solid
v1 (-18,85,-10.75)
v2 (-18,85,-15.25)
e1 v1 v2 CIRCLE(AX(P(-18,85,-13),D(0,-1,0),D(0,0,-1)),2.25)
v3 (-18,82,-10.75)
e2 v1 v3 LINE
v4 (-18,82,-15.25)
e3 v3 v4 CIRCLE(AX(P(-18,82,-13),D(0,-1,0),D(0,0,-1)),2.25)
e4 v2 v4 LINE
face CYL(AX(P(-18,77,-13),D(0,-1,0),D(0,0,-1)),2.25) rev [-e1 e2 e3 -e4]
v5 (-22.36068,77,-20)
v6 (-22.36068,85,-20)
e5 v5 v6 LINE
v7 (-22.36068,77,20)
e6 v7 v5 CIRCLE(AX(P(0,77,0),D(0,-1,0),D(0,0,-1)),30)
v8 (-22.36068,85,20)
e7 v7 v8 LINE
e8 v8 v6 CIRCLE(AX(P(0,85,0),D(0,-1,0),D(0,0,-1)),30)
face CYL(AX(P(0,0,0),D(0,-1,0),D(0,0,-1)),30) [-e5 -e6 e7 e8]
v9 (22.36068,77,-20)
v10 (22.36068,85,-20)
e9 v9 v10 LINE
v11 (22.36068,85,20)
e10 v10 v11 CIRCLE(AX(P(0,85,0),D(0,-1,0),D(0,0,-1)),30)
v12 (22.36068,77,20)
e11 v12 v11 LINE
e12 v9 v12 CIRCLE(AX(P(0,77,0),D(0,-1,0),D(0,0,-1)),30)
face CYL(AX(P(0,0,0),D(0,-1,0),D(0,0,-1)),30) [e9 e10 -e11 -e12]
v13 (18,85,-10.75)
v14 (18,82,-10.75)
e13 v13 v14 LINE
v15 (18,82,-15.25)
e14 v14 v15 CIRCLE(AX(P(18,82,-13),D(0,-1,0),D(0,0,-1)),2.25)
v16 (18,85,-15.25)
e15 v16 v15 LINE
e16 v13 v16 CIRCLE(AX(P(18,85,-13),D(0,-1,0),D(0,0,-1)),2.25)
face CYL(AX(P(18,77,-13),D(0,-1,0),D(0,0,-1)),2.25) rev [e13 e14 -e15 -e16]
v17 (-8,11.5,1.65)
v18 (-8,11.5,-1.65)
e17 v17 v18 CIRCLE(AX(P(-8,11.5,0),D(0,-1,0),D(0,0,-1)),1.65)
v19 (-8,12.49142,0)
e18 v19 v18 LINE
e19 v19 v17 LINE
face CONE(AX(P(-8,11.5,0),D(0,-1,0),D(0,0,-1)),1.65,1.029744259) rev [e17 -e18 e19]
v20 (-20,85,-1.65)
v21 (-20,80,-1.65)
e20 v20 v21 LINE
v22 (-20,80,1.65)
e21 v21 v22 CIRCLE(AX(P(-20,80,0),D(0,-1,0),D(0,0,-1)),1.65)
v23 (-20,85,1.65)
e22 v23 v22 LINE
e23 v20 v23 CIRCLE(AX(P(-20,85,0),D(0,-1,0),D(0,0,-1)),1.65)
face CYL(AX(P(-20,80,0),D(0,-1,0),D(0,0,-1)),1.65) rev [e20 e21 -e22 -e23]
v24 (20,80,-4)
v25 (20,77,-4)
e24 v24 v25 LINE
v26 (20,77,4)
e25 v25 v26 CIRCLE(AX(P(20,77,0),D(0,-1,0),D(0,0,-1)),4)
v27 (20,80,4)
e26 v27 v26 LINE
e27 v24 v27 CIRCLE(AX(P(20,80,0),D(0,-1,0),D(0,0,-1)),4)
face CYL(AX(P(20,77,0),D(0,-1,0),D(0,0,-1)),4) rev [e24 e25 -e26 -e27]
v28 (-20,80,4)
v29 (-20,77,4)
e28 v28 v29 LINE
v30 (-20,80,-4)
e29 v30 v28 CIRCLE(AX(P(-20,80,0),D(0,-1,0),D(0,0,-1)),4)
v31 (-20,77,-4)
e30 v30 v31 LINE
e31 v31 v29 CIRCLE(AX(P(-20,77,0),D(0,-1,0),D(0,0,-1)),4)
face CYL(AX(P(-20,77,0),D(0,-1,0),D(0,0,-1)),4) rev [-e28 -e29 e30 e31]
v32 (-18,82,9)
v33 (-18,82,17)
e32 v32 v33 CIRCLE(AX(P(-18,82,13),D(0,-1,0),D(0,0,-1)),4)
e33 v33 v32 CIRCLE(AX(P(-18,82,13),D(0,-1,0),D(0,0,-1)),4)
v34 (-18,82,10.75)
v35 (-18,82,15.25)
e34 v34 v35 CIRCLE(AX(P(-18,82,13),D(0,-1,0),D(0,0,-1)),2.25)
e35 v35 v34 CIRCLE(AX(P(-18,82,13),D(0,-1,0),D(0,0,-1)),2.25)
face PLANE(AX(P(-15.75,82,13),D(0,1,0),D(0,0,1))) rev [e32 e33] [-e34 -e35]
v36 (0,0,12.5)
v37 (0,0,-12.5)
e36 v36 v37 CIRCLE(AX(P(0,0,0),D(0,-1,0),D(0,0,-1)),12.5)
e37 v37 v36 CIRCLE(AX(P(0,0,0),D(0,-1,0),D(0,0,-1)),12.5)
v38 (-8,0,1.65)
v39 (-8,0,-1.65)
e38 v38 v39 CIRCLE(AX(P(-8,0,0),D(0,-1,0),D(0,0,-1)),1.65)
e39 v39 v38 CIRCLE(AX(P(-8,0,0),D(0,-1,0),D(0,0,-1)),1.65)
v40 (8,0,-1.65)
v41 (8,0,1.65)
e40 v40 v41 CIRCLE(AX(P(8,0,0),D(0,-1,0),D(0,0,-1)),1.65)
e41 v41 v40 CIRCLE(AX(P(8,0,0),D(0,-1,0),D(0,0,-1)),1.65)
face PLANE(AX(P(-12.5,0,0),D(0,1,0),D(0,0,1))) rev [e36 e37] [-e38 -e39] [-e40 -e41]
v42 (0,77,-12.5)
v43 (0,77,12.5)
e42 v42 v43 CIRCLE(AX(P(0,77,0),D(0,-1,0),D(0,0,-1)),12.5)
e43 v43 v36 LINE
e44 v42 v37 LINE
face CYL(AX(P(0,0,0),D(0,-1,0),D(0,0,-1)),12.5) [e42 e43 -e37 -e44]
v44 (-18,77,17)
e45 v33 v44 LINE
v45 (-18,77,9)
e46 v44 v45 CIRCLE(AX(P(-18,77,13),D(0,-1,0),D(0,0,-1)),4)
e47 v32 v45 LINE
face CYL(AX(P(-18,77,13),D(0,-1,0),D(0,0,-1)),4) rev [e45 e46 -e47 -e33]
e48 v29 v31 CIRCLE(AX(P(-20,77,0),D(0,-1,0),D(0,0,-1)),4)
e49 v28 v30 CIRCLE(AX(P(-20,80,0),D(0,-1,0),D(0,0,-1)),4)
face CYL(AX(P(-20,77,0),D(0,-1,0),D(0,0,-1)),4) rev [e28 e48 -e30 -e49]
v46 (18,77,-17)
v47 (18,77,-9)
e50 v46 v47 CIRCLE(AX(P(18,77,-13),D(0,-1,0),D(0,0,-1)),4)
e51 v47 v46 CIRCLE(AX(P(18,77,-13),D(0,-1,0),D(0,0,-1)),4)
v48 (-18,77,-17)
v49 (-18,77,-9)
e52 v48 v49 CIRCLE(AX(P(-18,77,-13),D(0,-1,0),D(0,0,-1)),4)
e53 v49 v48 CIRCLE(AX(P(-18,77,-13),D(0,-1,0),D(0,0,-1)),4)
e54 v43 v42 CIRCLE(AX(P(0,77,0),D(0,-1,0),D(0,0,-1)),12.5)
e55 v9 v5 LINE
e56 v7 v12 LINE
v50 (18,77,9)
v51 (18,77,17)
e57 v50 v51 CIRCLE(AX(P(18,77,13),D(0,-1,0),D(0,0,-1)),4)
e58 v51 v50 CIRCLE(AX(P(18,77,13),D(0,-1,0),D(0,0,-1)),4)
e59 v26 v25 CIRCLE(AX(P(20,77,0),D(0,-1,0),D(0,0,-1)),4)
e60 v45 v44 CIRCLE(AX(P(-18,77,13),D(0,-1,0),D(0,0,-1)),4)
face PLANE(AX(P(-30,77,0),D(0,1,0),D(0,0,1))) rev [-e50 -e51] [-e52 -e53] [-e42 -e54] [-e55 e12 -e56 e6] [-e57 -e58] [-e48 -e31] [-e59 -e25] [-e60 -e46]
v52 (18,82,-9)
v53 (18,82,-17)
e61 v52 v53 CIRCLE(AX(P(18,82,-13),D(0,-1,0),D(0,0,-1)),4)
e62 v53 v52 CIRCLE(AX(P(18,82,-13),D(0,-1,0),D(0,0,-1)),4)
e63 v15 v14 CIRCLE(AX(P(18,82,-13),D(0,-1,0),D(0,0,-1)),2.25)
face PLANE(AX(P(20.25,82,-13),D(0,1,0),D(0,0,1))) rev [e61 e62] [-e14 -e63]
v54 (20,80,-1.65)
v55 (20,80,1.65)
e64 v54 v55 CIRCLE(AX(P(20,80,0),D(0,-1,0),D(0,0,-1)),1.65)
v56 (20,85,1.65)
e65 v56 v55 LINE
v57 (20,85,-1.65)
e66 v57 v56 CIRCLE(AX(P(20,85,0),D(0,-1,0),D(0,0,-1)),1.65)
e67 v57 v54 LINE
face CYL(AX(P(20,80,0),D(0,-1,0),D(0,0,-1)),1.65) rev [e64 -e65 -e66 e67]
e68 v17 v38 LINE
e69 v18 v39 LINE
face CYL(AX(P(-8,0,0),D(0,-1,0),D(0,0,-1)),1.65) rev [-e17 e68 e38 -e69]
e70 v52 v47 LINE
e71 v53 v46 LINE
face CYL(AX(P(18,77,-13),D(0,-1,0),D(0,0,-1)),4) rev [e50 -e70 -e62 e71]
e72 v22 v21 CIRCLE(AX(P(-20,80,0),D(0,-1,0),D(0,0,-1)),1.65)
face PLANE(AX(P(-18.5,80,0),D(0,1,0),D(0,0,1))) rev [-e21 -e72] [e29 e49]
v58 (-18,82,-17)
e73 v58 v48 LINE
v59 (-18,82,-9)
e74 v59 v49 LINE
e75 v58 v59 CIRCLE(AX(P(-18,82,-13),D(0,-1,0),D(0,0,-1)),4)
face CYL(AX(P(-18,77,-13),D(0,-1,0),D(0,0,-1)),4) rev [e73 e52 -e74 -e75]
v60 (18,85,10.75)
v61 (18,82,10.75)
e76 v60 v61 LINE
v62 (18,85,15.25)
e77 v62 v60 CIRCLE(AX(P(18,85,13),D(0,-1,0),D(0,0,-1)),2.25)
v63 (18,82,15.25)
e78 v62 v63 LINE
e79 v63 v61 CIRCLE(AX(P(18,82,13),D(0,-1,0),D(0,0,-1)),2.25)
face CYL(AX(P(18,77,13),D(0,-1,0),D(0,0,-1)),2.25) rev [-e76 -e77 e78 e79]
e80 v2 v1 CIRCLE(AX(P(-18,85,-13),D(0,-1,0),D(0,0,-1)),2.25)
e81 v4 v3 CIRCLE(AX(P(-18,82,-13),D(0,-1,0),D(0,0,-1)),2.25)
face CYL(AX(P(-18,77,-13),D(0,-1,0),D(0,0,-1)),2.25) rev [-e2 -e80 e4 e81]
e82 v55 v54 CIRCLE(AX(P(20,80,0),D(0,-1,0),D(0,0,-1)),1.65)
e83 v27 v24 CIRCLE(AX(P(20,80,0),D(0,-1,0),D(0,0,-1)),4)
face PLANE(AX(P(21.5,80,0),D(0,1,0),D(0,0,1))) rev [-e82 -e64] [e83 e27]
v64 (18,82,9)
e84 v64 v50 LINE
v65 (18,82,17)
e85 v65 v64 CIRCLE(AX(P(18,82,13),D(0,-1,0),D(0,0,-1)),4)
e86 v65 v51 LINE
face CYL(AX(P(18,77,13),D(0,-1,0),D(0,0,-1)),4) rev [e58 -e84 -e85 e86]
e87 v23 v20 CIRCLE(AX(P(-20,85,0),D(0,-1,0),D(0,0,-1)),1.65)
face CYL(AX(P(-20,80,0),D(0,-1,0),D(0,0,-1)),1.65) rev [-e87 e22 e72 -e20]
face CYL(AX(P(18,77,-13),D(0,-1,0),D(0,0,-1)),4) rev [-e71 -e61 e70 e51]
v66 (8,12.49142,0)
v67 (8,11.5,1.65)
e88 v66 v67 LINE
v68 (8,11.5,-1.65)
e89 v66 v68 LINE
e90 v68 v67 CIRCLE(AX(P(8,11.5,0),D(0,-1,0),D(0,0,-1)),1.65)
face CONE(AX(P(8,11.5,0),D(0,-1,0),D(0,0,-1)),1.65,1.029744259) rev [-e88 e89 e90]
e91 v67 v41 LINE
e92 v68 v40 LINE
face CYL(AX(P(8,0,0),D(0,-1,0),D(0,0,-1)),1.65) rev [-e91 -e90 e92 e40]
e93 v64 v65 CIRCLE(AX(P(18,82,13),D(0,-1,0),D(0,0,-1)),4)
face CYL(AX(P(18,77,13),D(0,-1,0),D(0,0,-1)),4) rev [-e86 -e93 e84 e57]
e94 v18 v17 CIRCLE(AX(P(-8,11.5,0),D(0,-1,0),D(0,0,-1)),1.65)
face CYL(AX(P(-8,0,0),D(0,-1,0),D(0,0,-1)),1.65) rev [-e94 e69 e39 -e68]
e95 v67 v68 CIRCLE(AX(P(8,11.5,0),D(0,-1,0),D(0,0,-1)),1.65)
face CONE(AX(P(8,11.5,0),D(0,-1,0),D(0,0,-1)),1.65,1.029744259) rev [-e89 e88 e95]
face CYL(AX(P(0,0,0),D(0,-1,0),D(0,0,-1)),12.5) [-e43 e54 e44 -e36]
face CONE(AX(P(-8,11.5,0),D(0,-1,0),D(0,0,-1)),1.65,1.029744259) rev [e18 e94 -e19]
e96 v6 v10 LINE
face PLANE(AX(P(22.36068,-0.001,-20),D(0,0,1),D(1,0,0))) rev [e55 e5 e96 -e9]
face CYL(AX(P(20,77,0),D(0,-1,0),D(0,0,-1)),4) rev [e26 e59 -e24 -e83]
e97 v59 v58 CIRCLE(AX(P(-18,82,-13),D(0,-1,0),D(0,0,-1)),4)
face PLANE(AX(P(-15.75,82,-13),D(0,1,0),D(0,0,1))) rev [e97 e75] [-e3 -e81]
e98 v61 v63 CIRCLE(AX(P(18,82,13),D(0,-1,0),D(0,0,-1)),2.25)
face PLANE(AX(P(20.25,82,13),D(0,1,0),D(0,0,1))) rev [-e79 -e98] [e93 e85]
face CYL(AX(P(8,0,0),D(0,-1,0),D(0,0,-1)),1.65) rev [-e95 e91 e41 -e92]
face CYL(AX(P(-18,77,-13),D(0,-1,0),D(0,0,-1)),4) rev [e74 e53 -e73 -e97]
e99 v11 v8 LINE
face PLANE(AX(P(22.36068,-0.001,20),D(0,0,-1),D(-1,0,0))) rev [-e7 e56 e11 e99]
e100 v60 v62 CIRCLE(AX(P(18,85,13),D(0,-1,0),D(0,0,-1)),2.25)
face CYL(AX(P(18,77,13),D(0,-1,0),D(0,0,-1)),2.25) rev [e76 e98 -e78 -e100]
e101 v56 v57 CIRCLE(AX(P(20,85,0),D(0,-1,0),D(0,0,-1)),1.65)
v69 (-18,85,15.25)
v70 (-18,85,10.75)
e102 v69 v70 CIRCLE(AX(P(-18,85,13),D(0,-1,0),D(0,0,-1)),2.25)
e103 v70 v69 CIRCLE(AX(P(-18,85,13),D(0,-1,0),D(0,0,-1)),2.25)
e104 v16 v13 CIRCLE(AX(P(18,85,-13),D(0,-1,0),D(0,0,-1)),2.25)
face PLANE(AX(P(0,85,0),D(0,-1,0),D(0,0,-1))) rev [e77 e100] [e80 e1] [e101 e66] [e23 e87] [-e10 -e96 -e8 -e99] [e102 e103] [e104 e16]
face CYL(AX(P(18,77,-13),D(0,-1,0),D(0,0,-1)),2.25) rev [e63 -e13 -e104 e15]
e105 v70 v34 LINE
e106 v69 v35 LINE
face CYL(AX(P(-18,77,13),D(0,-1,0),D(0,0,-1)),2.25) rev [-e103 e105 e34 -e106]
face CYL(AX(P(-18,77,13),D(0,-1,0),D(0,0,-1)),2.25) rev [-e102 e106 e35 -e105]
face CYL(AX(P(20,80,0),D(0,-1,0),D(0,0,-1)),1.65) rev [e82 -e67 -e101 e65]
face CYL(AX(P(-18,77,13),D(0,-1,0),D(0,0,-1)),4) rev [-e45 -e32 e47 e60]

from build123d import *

# Parameters (mm, degrees)
M4_TAPPED_HOLE1_D                       = 3.3
M4_TAPPED_HOLE1_DEPTH                   = 11.5
M4_TAPPED_HOLE1_TIP                     = 0.991420021
CUT_EXTRUDE2_REACH                      = 97
CBORE_FOR_M4_HEX_HEAD_BOLT1_D           = 3
CBORE_FOR_M4_HEX_HEAD_BOLT1_CBORE_D     = 8
CBORE_FOR_M4_HEX_HEAD_BOLT1_CBORE_DEPTH = 3
M4_TAPPED_HOLE4_D                       = 3.3
M4_TAPPED_HOLE4_DEPTH                   = 10.1
M4_TAPPED_HOLE4_TIP                     = 0.991420021
CBORE_FOR_M4_HEX_HEAD_BOLT2_D           = 4.5
CBORE_FOR_M4_HEX_HEAD_BOLT2_DEPTH       = 10.1
CBORE_FOR_M4_HEX_HEAD_BOLT2_CBORE_D     = 8
CBORE_FOR_M4_HEX_HEAD_BOLT2_CBORE_DEPTH = 5
CBORE_FOR_M4_HEX_HEAD_BOLT2_TIP         = 1.351936393


with BuildPart() as part:
    # Sketch1 → Revolve1 (revolve)
    with BuildSketch(Plane.XY, mode=Mode.PRIVATE) as revolve1_sk:
        Polygon((0, 85), (-30, 85), (-30, 77), (-12.5, 77), (-12.5, 0), (0, 0), align=None)
    revolve(revolve1_sk.sketch.rotate(Axis((0, 0, 0), (0, 1, 0)), 270), axis=Axis((0, 0, 0), (0, 1, 0)))

    # M4 Tapped Hole1
    with Locations(Plane(origin=(-8, 0, 0), x_dir=(0, 0, -1), z_dir=(0, -1, 0))):
        with Locations((0, 0), (0, 16)):
            Hole(M4_TAPPED_HOLE1_D / 2, depth=M4_TAPPED_HOLE1_DEPTH)
            with Locations((0, 0, -(M4_TAPPED_HOLE1_DEPTH + M4_TAPPED_HOLE1_TIP / 2))):  # 118° drill point
                Cone(0, M4_TAPPED_HOLE1_D / 2, M4_TAPPED_HOLE1_TIP, mode=Mode.SUBTRACT)

    # Sketch4 → Cut-Extrude2 (cut, up to next)
    with BuildSketch(Plane(origin=(0, 85, 0), x_dir=(1, 0, 0), z_dir=(0, 1, 0)), mode=Mode.PRIVATE) as cut_extrude2_sk1:
        with BuildLine():
            Line((22.360679775, 20), (-22.360679775, 20))
            ThreePointArc((-22.360679775, 20), (0, 30), (22.360679775, 20))
        make_face()
    cut_extrude2_tool1 = extrude(cut_extrude2_sk1.sketch, amount=-CUT_EXTRUDE2_REACH, mode=Mode.PRIVATE) & part.part
    # Sketch4 → Cut-Extrude2 (cut, up to next)
    with BuildSketch(Plane(origin=(0, 85, 0), x_dir=(1, 0, 0), z_dir=(0, 1, 0)), mode=Mode.PRIVATE) as cut_extrude2_sk2:
        with BuildLine():
            Line((22.360679775, -20), (-22.360679775, -20))
            ThreePointArc((-22.360679775, -20), (0, -30), (22.360679775, -20))
        make_face()
    cut_extrude2_tool2 = extrude(cut_extrude2_sk2.sketch, amount=-CUT_EXTRUDE2_REACH, mode=Mode.PRIVATE) & part.part
    add(cut_extrude2_tool1.solids().sort_by_distance((0, 85, -24.063287))[0], mode=Mode.SUBTRACT)
    add(cut_extrude2_tool2.solids().sort_by_distance((0, 85, 24.063287))[0], mode=Mode.SUBTRACT)

    # CBORE for M4 Hex Head Bolt1 (through all)
    with Locations(Plane(origin=(-20, 77, 0), x_dir=(0, 0, -1), z_dir=(0, -1, 0))):
        with Locations((0, 0), (0, 40)):
            CounterBoreHole(CBORE_FOR_M4_HEX_HEAD_BOLT1_D / 2, CBORE_FOR_M4_HEX_HEAD_BOLT1_CBORE_D / 2, CBORE_FOR_M4_HEX_HEAD_BOLT1_CBORE_DEPTH)

    # M4 Tapped Hole4
    with Locations(Plane(origin=(-20, 80, 0), x_dir=(0, 0, -1), z_dir=(0, -1, 0))):
        with Locations((0, 0), (0, 40)):
            Hole(M4_TAPPED_HOLE4_D / 2, depth=M4_TAPPED_HOLE4_DEPTH)
            with Locations((0, 0, -(M4_TAPPED_HOLE4_DEPTH + M4_TAPPED_HOLE4_TIP / 2))):  # 118° drill point
                Cone(0, M4_TAPPED_HOLE4_D / 2, M4_TAPPED_HOLE4_TIP, mode=Mode.SUBTRACT)

    # CBORE for M4 Hex Head Bolt2
    with Locations(Plane(origin=(-18, 77, 13), x_dir=(0, 0, -1), z_dir=(0, -1, 0))):
        with Locations((0, 0), (0, 36), (26, 36), (26, 0)):
            CounterBoreHole(CBORE_FOR_M4_HEX_HEAD_BOLT2_D / 2, CBORE_FOR_M4_HEX_HEAD_BOLT2_CBORE_D / 2, CBORE_FOR_M4_HEX_HEAD_BOLT2_CBORE_DEPTH, depth=CBORE_FOR_M4_HEX_HEAD_BOLT2_DEPTH)
            with Locations((0, 0, -(CBORE_FOR_M4_HEX_HEAD_BOLT2_DEPTH + CBORE_FOR_M4_HEX_HEAD_BOLT2_TIP / 2))):  # 118° drill point
                Cone(0, CBORE_FOR_M4_HEX_HEAD_BOLT2_D / 2, CBORE_FOR_M4_HEX_HEAD_BOLT2_TIP, mode=Mode.SUBTRACT)


solid = part.part
